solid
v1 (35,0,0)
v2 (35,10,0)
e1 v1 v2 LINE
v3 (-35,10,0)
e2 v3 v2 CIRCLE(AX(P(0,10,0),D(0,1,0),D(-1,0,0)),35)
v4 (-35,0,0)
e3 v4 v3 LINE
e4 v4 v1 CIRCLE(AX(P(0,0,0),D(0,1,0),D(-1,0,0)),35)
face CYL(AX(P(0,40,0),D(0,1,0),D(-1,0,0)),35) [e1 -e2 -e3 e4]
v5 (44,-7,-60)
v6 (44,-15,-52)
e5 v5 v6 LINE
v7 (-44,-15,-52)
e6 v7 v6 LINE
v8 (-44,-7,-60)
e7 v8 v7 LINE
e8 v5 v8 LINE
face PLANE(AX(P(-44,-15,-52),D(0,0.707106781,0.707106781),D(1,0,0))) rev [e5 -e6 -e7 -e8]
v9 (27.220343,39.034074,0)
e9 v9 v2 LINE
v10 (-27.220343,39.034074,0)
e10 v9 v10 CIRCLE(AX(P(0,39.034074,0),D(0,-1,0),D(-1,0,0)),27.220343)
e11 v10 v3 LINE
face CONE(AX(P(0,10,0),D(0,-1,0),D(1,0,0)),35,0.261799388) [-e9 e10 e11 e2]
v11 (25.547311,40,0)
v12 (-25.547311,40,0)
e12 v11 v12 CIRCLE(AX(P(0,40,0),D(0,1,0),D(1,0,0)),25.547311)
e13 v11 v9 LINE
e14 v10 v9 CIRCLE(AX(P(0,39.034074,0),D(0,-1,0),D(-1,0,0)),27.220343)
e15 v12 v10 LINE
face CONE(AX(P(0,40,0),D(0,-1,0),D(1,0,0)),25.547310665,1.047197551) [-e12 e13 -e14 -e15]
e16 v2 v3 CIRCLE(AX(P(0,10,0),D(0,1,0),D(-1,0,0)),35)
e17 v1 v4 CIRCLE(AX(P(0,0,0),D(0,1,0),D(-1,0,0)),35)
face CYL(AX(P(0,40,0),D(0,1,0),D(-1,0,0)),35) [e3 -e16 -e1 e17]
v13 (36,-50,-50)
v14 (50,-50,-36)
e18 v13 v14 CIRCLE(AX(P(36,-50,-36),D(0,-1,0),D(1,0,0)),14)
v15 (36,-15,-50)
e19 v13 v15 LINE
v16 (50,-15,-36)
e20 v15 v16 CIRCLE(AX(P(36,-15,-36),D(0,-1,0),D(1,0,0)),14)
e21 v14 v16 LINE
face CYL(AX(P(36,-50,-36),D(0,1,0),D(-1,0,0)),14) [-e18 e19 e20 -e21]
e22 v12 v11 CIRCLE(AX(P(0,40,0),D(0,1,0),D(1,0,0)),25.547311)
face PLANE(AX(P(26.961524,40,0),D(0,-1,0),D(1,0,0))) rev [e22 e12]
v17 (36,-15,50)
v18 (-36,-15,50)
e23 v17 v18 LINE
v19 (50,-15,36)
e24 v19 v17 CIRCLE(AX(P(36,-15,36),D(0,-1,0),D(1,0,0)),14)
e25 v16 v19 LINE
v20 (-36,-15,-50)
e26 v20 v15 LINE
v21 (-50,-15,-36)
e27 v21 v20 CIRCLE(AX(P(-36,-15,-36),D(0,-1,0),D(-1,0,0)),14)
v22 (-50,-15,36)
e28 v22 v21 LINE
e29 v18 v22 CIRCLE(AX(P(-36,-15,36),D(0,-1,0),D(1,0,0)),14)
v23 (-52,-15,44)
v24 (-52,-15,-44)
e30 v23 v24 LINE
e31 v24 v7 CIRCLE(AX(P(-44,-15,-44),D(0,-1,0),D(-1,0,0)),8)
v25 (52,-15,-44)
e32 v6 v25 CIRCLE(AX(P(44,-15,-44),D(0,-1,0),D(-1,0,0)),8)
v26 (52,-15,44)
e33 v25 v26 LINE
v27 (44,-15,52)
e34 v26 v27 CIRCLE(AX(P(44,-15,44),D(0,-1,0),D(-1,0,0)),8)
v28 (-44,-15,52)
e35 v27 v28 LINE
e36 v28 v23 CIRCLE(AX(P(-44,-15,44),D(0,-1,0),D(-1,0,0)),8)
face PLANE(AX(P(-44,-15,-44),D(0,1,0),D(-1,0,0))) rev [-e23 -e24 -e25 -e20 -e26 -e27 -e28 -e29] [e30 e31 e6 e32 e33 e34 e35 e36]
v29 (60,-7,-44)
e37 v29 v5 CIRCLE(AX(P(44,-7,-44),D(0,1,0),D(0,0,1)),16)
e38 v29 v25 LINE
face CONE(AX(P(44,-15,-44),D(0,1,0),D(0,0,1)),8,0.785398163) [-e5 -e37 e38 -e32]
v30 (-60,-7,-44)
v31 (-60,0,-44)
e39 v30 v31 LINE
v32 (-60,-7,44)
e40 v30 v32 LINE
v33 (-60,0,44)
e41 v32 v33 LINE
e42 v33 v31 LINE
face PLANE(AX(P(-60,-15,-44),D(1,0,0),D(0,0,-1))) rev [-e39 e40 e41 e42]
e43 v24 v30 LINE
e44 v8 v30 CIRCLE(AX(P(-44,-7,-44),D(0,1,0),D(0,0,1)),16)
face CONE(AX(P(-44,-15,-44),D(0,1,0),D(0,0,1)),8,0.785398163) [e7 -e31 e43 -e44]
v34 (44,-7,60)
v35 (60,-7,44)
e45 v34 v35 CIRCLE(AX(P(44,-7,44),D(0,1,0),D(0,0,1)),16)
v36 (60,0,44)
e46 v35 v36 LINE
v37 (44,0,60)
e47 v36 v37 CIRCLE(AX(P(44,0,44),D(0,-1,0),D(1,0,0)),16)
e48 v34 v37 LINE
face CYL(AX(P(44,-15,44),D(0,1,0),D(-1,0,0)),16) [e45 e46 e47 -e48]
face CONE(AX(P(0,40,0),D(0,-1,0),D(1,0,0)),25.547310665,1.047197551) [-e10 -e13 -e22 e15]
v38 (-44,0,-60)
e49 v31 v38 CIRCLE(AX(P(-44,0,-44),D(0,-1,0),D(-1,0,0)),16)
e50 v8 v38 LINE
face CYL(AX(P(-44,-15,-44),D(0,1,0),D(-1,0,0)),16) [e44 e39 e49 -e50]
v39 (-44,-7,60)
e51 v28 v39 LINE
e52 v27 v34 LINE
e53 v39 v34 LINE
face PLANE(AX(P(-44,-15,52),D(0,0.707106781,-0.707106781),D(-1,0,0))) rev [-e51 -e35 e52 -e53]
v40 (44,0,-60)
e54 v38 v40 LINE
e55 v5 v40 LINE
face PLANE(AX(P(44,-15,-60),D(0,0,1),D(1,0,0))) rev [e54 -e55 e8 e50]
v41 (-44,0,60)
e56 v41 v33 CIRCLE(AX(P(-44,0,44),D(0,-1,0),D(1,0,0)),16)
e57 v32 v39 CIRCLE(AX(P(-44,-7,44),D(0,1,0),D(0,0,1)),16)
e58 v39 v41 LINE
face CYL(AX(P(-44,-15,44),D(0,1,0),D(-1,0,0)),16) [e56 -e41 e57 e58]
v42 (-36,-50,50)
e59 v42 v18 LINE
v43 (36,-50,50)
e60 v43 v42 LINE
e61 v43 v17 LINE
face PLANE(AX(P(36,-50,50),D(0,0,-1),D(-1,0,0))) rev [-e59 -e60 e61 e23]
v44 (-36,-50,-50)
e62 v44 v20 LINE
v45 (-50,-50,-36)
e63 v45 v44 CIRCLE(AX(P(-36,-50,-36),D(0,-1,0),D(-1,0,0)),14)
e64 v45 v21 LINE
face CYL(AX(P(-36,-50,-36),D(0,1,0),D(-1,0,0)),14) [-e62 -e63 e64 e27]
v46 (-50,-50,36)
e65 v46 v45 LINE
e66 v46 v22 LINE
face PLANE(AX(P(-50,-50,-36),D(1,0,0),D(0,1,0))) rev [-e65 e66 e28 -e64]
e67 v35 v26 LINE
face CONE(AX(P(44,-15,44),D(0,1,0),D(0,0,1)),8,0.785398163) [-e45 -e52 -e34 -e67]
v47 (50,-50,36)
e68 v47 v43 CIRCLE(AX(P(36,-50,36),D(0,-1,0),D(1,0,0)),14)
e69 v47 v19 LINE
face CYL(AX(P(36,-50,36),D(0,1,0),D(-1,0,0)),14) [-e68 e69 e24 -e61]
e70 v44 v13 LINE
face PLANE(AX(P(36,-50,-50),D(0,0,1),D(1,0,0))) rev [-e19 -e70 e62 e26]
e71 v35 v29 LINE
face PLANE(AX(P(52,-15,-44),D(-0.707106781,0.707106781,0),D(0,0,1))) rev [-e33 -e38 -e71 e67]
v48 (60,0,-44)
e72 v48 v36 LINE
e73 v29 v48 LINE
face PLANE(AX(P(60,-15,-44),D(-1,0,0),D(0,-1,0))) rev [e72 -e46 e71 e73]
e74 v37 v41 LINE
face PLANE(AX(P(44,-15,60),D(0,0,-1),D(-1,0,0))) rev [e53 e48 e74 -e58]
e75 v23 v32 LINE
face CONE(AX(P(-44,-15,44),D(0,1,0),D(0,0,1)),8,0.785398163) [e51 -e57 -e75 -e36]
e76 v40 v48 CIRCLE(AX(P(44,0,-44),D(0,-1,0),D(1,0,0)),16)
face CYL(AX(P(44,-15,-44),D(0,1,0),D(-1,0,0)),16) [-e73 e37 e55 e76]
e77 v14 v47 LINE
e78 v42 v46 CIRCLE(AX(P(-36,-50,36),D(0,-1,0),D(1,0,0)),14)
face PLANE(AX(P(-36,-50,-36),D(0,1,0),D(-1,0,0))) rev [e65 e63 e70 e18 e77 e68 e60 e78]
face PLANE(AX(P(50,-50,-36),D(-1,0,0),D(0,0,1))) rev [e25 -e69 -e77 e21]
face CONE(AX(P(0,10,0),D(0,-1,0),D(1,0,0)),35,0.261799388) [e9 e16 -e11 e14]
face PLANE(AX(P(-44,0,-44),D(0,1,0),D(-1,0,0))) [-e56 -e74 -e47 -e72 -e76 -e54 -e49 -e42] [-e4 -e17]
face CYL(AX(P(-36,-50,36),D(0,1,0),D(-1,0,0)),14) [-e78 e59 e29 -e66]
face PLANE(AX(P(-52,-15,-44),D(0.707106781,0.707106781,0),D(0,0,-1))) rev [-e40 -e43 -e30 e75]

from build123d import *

# Parameters (mm, degrees)
CHAMFER_1_SIZE  = 1
CHAMFER_1_SIZE2 = 1.414213562
EXTRUDE_1_DEPTH = 15
EXTRUDE_2_DEPTH = 35
CHAMFER_2_SIZE  = 8


with BuildPart() as part:
    # 草图1 → 旋转1 (revolve)
    with BuildSketch(Plane.XY, mode=Mode.PRIVATE) as revolve_1_sk:
        Polygon((0, 0), (35, 0), (35, 10), (26.961524227, 40), (0, 40), align=None)
    revolve(revolve_1_sk.sketch.rotate(Axis((0, 40, 0), (0, -1, 0)), 180), axis=Axis((0, 40, 0), (0, -1, 0)))

    # 倒角1
    chamfer_1_edges = [part.edges().sort_by_distance(p)[0] for p in [
        (26.961524227, 40, 0),
    ]]
    chamfer_1_side = [part.faces().sort_by_distance(p)[0] for p in [
        (30.980762114, 25, 0),
    ]]
    chamfer(chamfer_1_edges, length=CHAMFER_1_SIZE, length2=CHAMFER_1_SIZE2, reference=chamfer_1_side[0])

    # 草图2 → 凸台-拉伸1 (add)
    with BuildSketch(Plane.XZ):
        with BuildLine():
            Line((44, -60), (-44, -60))
            ThreePointArc((-44, -60), (-55.313708499, -55.313708499), (-60, -44))
            Line((-60, -44), (-60, 44))
            ThreePointArc((-60, 44), (-55.313708499, 55.313708499), (-44, 60))
            Line((-44, 60), (44, 60))
            ThreePointArc((44, 60), (55.313708499, 55.313708499), (60, 44))
            Line((60, 44), (60, -44))
            ThreePointArc((60, -44), (55.313708499, -55.313708499), (44, -60))
        make_face()
    extrude(amount=EXTRUDE_1_DEPTH)

    # 草图3 → 凸台-拉伸2 (add)
    with BuildSketch(Plane.XZ.offset(15)):
        with BuildLine():
            Line((36, -50), (-36, -50))
            ThreePointArc((-36, -50), (-45.899494937, -45.899494937), (-50, -36))
            Line((-50, -36), (-50, 36))
            ThreePointArc((-50, 36), (-45.899494937, 45.899494937), (-36, 50))
            Line((-36, 50), (36, 50))
            ThreePointArc((36, 50), (45.899494937, 45.899494937), (50, 36))
            Line((50, 36), (50, -36))
            ThreePointArc((50, -36), (45.899494937, -45.899494937), (36, -50))
        make_face()
    extrude(amount=EXTRUDE_2_DEPTH)

    # 倒角2
    chamfer_2_edges = [part.edges().sort_by_distance(p)[0] for p in [
        (-55.313708499, -15, -55.313708499),
        (0, -15, -60),
        (55.313708499, -15, -55.313708499),
        (60, -15, 0),
        (55.313708499, -15, 55.313708499),
        (0, -15, 60),
        (-55.313708499, -15, 55.313708499),
        (-60, -15, 0),
    ]]
    chamfer(chamfer_2_edges, length=CHAMFER_2_SIZE)


solid = part.part
